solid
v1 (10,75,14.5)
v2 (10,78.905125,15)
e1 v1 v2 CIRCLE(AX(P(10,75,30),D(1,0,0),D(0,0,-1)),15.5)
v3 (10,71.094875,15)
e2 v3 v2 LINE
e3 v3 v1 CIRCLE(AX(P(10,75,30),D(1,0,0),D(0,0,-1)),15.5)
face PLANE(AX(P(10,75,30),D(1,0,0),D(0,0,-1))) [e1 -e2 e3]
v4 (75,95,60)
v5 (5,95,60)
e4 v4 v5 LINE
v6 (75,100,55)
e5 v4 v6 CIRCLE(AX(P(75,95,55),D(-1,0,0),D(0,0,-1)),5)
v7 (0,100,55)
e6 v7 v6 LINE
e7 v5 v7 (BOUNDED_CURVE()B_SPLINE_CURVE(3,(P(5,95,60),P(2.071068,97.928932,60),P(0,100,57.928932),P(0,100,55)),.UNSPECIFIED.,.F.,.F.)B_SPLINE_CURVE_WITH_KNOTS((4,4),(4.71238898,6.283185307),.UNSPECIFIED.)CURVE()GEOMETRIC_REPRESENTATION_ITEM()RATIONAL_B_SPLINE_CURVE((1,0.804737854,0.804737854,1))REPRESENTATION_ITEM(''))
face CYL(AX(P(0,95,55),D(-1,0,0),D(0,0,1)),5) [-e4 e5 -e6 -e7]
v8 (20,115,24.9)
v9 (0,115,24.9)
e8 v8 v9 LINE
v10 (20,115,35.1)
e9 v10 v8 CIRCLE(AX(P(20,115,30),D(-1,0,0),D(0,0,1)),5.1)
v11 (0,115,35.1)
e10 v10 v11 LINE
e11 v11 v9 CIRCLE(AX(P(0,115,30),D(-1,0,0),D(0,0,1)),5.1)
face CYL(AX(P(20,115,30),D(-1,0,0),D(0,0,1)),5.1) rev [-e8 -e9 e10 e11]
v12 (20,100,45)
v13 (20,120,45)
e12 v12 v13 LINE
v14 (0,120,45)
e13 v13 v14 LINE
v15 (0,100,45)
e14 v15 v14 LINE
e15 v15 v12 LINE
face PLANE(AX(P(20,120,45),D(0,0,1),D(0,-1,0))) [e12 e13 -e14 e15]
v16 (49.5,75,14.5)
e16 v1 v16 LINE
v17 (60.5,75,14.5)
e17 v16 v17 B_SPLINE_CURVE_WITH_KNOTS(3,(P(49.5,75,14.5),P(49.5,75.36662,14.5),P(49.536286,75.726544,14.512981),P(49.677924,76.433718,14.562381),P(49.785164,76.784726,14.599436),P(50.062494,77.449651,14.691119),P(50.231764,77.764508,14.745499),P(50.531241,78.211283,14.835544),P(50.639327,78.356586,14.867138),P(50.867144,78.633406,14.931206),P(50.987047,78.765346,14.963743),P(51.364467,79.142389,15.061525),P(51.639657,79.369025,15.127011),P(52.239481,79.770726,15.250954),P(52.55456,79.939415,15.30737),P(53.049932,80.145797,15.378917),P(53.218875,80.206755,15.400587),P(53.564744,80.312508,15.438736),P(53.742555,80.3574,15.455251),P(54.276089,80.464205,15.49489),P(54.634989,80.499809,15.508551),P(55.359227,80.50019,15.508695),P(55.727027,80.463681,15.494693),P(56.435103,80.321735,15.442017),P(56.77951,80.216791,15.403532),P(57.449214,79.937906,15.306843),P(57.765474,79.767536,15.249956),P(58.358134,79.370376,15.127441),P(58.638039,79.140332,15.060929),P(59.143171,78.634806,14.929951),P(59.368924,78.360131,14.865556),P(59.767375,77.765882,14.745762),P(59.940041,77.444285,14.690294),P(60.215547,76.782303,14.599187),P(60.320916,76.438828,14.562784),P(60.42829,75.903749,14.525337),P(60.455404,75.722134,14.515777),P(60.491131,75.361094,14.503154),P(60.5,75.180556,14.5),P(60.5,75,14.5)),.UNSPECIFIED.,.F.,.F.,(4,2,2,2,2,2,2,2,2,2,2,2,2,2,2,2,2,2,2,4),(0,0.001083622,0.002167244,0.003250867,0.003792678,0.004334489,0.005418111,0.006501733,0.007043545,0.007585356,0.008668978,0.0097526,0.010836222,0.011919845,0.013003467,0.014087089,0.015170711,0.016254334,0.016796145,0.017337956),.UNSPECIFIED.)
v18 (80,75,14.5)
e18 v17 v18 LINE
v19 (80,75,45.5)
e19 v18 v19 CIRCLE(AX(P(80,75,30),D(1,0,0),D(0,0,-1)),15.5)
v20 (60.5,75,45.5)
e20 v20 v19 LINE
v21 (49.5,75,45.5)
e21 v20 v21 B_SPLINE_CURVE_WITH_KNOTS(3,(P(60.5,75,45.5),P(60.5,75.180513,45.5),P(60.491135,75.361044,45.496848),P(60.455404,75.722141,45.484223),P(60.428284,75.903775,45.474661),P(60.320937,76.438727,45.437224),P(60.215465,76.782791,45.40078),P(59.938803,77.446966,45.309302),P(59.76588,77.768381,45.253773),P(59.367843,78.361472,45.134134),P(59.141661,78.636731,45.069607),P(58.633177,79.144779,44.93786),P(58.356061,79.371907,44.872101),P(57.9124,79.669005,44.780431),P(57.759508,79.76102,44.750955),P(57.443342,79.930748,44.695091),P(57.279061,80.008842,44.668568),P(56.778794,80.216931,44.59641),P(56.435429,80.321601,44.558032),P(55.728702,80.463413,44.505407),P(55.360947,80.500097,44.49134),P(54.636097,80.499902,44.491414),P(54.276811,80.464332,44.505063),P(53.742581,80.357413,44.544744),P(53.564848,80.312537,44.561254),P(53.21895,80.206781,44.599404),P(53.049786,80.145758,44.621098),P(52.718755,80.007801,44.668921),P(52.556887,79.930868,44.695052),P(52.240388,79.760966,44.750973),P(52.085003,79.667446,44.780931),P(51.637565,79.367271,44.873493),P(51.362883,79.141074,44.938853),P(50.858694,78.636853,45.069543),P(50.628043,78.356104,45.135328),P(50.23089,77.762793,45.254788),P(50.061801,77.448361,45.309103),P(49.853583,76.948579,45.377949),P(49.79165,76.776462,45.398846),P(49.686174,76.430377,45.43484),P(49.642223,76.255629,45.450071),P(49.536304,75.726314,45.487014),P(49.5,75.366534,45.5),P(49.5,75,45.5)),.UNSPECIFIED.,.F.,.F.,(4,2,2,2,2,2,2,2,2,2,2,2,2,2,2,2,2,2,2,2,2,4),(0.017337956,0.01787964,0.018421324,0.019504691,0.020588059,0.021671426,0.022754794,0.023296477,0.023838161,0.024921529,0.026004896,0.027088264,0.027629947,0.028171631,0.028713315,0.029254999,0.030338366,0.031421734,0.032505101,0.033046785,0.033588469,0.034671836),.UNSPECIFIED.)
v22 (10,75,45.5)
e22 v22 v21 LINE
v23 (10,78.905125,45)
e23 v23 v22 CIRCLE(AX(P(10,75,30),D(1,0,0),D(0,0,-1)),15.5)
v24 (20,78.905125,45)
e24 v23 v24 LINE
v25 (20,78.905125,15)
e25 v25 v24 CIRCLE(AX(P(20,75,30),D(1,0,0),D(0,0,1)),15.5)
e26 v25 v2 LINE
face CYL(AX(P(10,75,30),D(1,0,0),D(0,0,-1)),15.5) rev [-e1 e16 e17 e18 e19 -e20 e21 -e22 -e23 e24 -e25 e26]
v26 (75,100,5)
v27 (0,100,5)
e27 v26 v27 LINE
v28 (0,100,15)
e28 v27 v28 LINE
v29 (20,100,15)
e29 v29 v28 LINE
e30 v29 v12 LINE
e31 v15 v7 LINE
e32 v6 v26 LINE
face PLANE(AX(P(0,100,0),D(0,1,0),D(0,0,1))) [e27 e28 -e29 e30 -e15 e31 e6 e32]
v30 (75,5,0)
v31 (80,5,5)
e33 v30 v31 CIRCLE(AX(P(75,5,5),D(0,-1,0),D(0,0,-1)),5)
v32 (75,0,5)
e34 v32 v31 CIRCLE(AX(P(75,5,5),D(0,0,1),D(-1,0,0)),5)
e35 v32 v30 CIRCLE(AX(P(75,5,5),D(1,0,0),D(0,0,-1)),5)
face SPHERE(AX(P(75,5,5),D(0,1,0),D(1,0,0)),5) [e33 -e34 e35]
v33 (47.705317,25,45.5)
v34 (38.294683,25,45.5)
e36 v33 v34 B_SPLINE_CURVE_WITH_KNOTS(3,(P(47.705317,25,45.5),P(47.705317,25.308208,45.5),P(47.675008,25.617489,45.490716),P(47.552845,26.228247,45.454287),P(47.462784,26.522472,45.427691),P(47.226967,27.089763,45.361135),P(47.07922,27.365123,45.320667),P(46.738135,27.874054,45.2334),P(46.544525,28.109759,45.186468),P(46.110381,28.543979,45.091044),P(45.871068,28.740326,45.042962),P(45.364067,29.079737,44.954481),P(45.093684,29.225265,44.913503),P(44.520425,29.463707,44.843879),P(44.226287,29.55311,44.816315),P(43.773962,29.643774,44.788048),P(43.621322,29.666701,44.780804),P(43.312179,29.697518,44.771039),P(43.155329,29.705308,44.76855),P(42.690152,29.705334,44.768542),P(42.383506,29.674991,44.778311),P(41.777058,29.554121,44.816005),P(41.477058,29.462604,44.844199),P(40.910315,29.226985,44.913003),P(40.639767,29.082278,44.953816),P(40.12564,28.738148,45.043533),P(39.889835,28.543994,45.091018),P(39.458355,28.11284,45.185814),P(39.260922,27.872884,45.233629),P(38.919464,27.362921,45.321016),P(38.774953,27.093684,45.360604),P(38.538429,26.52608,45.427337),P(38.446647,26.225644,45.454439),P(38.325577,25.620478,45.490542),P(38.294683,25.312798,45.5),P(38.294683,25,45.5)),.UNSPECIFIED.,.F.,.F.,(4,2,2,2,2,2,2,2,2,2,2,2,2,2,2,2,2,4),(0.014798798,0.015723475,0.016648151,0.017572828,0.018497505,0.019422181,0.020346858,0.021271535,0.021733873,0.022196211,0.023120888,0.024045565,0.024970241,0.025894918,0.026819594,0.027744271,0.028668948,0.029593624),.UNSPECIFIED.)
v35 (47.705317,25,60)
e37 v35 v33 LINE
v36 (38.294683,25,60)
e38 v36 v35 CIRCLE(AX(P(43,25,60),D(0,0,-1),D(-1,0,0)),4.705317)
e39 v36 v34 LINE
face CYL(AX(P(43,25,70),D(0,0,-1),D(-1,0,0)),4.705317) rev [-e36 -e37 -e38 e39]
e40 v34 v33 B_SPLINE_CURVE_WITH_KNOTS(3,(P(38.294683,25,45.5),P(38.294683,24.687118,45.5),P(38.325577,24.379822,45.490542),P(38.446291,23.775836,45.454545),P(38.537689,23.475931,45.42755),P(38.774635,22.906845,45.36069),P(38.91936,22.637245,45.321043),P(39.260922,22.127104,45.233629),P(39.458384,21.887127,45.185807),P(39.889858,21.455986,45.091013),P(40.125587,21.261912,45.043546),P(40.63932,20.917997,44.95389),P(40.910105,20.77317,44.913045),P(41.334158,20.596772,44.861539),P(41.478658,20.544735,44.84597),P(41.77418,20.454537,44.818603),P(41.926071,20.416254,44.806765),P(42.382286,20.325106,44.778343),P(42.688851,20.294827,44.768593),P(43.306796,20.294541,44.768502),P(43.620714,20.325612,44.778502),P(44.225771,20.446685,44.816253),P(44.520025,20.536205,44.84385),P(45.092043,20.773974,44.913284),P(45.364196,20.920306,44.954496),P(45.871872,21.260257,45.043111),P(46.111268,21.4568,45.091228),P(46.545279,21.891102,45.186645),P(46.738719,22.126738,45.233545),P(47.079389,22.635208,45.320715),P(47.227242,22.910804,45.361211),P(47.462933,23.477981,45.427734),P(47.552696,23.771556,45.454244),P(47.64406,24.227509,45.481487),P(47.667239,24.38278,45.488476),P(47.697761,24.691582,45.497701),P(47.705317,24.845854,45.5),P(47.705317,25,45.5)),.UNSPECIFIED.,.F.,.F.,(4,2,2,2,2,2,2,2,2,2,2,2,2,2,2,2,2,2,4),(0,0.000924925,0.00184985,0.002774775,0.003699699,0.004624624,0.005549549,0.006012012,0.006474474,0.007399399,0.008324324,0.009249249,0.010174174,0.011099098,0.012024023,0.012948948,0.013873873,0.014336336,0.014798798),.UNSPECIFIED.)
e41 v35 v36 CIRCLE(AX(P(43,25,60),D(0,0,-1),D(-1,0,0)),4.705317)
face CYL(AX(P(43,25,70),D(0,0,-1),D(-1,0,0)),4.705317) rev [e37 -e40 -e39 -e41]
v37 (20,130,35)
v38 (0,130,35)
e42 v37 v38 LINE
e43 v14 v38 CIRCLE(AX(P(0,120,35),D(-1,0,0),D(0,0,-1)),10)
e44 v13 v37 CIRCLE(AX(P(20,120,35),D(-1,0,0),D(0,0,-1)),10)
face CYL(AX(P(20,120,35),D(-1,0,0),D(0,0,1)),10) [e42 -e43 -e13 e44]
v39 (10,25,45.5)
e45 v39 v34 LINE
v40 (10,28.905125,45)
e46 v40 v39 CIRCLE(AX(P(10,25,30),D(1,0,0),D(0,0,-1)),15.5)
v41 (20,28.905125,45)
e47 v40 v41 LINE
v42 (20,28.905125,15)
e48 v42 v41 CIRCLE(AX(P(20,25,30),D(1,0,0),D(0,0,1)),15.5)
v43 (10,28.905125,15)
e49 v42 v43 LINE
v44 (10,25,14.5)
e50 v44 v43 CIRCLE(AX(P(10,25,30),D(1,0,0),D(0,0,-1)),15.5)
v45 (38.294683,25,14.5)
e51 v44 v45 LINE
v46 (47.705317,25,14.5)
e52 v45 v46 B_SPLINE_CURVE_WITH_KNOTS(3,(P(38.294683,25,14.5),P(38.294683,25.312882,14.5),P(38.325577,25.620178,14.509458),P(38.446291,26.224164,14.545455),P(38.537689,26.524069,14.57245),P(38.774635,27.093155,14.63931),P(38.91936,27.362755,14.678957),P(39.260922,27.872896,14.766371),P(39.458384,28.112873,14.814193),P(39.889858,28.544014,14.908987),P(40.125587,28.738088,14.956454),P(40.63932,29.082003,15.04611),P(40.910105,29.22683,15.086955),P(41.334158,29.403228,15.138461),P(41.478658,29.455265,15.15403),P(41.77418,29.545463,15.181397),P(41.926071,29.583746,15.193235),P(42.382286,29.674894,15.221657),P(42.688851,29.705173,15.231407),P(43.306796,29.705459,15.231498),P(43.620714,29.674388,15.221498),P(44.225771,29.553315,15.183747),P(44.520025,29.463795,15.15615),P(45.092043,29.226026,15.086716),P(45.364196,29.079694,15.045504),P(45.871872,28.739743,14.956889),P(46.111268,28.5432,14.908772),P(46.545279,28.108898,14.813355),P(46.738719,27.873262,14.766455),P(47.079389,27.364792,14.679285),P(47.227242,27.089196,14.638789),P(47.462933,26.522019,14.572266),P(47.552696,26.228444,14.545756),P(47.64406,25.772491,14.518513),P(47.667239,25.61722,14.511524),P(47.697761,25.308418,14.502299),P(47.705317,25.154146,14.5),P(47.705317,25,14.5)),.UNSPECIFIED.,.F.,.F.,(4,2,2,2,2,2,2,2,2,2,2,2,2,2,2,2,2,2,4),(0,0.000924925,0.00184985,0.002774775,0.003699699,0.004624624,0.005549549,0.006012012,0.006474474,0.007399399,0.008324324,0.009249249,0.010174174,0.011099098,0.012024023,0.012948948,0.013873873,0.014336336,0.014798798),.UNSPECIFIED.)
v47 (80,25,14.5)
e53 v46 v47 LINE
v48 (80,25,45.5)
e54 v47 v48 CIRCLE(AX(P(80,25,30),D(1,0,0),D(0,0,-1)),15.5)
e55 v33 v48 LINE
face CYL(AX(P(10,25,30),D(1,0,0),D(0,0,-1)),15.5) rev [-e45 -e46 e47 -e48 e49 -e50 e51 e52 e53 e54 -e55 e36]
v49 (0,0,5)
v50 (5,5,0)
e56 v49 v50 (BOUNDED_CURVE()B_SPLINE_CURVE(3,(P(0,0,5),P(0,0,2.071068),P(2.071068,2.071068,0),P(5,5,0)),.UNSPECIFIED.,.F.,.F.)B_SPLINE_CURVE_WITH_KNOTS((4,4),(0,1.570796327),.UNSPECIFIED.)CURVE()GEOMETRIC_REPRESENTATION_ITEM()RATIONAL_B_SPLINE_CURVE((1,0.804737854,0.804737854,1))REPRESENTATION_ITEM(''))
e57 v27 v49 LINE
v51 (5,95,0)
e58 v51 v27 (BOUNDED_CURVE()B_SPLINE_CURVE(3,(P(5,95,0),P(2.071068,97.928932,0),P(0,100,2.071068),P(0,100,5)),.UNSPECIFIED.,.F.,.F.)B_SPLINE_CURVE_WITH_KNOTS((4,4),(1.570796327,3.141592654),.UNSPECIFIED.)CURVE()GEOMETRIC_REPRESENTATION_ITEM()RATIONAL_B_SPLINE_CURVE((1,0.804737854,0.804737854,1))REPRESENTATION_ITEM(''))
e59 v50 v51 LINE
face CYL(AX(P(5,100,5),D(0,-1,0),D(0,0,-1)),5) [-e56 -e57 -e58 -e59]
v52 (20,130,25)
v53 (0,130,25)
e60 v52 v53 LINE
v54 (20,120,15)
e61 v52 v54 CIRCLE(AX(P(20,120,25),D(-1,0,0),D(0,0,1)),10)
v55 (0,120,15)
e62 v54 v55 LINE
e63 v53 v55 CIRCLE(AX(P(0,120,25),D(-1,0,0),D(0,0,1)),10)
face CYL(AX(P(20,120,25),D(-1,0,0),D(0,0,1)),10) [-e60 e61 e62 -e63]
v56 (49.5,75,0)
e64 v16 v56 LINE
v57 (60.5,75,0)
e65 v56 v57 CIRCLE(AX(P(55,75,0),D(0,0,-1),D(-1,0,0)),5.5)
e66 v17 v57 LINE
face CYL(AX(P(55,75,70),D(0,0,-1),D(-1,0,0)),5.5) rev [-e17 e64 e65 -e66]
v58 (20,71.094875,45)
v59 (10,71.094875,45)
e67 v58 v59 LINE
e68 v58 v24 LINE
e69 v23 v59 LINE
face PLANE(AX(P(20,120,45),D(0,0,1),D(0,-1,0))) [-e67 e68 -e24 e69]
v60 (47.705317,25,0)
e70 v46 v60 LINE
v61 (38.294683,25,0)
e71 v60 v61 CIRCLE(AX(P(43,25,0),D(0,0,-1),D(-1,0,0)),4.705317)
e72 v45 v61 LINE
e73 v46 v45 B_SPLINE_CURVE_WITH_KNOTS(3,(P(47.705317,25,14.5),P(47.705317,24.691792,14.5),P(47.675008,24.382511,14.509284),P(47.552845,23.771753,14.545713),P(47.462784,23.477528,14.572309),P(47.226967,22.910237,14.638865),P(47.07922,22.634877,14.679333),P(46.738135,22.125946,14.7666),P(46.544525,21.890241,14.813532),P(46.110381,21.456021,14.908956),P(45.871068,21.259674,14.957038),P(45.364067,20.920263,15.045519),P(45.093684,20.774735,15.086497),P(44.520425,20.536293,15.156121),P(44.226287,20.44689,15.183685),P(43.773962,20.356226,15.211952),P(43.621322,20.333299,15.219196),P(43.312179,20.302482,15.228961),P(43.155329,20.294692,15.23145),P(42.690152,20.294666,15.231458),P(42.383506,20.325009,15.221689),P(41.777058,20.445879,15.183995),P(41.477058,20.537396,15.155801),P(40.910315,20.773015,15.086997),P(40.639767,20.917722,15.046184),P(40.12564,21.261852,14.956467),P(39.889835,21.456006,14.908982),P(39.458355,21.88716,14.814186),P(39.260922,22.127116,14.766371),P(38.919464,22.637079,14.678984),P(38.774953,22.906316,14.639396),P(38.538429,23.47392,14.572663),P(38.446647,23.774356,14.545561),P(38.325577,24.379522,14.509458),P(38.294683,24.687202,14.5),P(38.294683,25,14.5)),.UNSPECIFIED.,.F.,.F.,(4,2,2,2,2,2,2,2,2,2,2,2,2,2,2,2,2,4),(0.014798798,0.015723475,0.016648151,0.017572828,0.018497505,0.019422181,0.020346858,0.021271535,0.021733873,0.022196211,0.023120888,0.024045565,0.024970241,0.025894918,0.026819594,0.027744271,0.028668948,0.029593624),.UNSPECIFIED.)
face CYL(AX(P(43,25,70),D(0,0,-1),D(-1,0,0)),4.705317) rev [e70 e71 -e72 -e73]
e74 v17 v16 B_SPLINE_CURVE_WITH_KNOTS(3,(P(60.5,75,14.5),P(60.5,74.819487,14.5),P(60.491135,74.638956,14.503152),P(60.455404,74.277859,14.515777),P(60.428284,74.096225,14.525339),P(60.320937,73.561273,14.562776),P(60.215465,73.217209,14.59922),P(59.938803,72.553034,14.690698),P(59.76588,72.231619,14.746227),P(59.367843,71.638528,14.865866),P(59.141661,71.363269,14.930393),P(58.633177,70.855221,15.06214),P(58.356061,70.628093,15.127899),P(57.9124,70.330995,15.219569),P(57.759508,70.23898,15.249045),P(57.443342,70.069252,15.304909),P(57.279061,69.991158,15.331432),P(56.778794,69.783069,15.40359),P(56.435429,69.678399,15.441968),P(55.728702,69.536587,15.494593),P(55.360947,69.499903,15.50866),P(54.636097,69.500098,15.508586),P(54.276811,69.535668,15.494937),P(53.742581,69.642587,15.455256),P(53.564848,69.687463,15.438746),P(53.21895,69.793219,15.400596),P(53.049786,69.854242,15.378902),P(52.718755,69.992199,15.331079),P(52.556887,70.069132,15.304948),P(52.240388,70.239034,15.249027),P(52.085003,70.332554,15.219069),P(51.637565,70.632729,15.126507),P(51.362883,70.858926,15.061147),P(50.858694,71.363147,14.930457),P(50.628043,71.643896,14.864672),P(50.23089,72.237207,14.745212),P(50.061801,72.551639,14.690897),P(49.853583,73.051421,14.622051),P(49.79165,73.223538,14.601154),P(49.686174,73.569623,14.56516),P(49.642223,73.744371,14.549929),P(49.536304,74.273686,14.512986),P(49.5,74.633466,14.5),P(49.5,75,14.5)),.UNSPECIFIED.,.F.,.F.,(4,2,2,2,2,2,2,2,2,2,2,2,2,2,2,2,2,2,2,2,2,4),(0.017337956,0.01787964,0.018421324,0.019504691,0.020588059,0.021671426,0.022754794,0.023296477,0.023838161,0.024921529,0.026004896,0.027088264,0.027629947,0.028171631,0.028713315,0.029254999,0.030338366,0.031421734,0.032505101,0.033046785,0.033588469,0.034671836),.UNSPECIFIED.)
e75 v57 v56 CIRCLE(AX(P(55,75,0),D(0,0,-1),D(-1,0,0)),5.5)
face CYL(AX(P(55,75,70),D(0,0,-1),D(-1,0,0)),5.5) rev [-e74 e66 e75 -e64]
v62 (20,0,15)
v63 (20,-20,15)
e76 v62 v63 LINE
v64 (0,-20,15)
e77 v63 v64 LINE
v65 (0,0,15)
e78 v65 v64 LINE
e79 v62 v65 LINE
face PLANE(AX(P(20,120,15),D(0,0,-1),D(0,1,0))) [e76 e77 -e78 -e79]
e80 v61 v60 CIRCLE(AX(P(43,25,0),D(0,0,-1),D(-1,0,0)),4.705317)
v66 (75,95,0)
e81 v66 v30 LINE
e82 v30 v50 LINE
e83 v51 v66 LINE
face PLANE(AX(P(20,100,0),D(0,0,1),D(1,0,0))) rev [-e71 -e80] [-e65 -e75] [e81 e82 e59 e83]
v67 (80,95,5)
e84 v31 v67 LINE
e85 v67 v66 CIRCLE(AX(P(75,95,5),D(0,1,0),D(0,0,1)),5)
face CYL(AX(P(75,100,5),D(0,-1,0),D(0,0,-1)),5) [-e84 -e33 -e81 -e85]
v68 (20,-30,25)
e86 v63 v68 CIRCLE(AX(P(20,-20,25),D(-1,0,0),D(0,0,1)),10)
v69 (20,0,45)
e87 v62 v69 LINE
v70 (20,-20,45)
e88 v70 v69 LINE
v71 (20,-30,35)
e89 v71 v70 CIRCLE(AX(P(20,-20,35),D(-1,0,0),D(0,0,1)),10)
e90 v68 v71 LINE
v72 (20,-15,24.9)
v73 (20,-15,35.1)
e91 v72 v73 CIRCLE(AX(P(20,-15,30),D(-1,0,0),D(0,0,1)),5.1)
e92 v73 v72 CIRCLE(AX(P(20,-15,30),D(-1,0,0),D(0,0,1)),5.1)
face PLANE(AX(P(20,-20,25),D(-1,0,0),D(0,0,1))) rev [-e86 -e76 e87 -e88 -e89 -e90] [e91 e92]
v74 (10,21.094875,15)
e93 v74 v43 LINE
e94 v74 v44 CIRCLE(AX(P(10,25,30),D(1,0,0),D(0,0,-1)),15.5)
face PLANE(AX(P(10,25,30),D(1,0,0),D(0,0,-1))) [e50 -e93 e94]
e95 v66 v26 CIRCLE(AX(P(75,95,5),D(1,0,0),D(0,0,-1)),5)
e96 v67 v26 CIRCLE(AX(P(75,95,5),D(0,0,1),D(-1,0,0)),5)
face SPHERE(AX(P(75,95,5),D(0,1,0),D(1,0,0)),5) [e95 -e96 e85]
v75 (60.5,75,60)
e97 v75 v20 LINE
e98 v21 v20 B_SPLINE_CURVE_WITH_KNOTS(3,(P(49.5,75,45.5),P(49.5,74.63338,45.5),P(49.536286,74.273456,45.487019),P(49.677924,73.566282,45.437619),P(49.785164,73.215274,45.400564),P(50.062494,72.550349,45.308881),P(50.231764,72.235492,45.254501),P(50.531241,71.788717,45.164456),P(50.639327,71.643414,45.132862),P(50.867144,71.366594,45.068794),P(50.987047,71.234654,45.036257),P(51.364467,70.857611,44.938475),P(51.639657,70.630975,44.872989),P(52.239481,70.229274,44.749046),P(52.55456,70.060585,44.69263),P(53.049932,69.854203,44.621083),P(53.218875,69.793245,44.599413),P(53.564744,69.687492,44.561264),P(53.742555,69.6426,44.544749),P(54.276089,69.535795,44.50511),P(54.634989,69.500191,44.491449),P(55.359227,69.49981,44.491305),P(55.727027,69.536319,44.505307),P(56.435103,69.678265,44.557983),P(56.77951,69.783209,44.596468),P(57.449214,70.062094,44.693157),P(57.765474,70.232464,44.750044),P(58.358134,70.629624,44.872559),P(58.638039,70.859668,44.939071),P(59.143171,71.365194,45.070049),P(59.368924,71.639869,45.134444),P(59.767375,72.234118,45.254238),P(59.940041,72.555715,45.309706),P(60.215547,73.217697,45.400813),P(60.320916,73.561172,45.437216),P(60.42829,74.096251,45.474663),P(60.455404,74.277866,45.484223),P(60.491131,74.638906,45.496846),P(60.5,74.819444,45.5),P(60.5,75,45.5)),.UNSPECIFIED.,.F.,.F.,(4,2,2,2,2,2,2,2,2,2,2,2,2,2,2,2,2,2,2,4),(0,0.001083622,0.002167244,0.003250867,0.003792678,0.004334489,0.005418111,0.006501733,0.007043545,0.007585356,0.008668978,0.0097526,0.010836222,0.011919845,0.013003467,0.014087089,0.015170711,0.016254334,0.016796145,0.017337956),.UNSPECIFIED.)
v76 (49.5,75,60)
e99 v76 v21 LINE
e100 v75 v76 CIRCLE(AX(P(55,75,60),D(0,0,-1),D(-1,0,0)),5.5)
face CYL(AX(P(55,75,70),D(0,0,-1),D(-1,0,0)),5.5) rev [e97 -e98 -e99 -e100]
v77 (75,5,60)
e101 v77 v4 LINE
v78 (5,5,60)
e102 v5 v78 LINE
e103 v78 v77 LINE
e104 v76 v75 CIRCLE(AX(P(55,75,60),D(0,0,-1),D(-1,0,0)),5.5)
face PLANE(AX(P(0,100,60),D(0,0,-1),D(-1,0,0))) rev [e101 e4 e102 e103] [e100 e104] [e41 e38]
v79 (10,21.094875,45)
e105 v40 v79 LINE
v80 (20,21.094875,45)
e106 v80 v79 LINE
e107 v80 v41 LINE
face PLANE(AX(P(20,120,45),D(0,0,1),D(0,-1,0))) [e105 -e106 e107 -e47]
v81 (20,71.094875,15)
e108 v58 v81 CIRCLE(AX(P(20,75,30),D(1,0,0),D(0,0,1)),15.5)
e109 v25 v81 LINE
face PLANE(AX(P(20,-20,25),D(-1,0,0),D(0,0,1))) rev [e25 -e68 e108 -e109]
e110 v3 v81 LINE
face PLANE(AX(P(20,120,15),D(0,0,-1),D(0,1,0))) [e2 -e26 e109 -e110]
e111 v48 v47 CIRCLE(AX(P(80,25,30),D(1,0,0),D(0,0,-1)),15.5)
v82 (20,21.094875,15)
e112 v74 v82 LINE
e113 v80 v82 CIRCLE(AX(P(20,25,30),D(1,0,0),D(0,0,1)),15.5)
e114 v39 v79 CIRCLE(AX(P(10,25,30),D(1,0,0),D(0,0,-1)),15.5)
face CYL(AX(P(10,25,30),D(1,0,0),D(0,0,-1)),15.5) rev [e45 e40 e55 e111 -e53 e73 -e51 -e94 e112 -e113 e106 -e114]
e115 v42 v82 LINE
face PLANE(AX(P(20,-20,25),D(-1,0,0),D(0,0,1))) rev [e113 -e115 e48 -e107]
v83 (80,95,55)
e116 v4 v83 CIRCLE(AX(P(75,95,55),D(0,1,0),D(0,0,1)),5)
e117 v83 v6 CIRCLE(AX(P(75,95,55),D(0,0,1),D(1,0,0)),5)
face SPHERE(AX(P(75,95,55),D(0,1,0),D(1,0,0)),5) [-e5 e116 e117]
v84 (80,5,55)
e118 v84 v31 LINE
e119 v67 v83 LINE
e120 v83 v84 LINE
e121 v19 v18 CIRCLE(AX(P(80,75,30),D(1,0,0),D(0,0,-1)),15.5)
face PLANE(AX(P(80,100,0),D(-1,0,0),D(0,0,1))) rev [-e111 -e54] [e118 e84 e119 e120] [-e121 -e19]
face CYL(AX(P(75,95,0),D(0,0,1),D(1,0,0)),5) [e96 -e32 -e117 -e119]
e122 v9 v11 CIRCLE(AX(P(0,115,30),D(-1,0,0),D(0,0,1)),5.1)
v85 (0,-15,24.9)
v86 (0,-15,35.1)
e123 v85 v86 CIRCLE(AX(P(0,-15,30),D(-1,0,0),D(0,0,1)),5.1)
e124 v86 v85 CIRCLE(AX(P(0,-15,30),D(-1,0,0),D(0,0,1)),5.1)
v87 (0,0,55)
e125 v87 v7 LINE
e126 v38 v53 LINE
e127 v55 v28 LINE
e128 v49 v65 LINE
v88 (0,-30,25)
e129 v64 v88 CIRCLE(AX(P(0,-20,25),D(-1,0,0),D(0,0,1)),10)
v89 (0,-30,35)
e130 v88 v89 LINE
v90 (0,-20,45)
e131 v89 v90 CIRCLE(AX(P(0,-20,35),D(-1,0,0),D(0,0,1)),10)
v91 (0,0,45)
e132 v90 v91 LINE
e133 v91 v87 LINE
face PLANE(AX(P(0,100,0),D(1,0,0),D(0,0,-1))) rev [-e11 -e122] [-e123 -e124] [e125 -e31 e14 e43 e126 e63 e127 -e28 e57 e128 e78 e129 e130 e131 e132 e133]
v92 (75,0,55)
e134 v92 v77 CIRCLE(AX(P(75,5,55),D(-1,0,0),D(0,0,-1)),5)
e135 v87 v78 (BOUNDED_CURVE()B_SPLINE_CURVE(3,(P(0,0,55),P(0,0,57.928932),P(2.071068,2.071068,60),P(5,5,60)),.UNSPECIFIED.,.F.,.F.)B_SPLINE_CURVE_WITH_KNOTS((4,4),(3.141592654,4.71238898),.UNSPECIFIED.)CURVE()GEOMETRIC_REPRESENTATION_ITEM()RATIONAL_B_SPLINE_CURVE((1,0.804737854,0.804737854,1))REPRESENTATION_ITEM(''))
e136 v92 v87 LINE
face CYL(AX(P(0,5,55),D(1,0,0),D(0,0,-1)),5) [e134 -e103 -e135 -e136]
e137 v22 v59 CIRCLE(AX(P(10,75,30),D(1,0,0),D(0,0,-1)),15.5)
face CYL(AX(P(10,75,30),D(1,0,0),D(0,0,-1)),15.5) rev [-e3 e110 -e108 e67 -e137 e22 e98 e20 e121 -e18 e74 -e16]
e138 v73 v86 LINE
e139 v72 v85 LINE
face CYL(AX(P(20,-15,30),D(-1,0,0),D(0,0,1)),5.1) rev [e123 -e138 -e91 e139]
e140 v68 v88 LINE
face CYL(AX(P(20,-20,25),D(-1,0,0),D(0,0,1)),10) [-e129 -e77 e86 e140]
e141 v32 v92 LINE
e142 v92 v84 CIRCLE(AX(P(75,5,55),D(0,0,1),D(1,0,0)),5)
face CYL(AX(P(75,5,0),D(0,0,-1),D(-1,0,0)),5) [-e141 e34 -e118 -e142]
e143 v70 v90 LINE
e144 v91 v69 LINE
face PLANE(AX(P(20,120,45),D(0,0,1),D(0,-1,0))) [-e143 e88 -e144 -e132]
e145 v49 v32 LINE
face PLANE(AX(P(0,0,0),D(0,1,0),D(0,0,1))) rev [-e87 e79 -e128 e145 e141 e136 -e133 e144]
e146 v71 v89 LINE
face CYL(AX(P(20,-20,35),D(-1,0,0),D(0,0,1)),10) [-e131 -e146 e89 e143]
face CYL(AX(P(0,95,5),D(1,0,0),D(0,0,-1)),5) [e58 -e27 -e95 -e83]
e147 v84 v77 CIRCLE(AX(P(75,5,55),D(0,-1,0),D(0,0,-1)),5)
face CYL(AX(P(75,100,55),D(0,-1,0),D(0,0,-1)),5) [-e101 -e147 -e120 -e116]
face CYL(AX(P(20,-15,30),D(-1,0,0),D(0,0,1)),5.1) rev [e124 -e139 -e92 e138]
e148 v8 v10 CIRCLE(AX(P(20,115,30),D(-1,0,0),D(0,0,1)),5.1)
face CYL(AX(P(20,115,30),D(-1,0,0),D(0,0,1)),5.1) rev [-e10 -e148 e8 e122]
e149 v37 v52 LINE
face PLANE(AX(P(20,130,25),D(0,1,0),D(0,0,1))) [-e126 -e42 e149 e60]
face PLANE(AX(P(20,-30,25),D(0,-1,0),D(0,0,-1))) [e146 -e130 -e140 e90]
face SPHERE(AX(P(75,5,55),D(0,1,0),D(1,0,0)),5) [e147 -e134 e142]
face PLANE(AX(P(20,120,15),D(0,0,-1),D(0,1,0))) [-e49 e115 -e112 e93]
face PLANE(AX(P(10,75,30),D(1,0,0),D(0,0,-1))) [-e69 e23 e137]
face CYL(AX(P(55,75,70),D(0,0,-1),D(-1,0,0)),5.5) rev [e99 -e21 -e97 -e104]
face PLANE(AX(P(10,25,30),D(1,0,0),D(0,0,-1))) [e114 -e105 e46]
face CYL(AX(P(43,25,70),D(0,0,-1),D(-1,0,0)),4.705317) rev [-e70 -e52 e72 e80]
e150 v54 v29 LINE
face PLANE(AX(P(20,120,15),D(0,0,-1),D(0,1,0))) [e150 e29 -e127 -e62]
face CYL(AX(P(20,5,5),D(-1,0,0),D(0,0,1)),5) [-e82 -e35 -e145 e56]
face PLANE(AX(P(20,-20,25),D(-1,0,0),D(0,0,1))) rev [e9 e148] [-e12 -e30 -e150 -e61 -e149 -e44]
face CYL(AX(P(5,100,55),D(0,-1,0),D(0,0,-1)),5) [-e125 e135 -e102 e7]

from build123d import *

# Parameters (mm, degrees)
BOSS_EXTRUDE1_DEPTH = 100
SKETCH2_R           = 15.5
CUT_EXTRUDE1_DEPTH  = 70
SKETCH3_R           = 5.1
CUT_EXTRUDE2_DEPTH  = 70
SKETCH4_R           = 5.5
SKETCH4_R_2         = 4.705316684
CUT_EXTRUDE3_DEPTH  = 70
SKETCH5_R           = 5.1
BOSS_EXTRUDE2_DEPTH = 20
SKETCH6_W           = 20
SKETCH6_H           = 100
CUT_EXTRUDE4_DEPTH  = 20
FILLET1_R           = 5


with BuildPart() as part:
    # Sketch1 → Boss-Extrude1 (new body)
    with BuildSketch(Plane(origin=(0, 0, 0), x_dir=(1, 0, 0), z_dir=(0, 1, 0))):
        Polygon((0, 20), (20, 20), (20, 0), (80, 0), (80, -60), (0, -60), (0, 0), align=None)
    extrude(amount=BOSS_EXTRUDE1_DEPTH)

    # Sketch2 → Cut-Extrude1 (cut)
    with BuildSketch(Plane(origin=(80, 0, 0), x_dir=(0, 0, -1), z_dir=(1, 0, 0))):
        with Locations((-30, 75)):
            Circle(SKETCH2_R)
        with Locations((-30, 25)):
            Circle(SKETCH2_R)
    extrude(amount=-CUT_EXTRUDE1_DEPTH, mode=Mode.SUBTRACT)

    # Sketch3 → Cut-Extrude2 (cut)
    with BuildSketch(Plane(origin=(20, 0, 0), x_dir=(0, 0, -1), z_dir=(1, 0, 0))):
        with Locations((10, 87.5)):
            Circle(SKETCH3_R)
        with Locations((10, 12.5)):
            Circle(SKETCH3_R)
        with Locations((10, 50)):
            Circle(SKETCH3_R)
    extrude(amount=-CUT_EXTRUDE2_DEPTH, mode=Mode.SUBTRACT)

    # Sketch4 → Cut-Extrude3 (cut)
    with BuildSketch(Plane(origin=(0, 0, 0), x_dir=(-1, 0, 0), z_dir=(0, 0, -1))):
        with Locations((-55, 75)):
            Circle(SKETCH4_R)
        with Locations((-43, 25)):
            Circle(SKETCH4_R_2)
    extrude(amount=-CUT_EXTRUDE3_DEPTH, mode=Mode.SUBTRACT)

    # Sketch5 → Boss-Extrude2 (add)
    with BuildSketch(Plane.ZY):
        with BuildLine():
            Line((25, 130), (35, 130))
            ThreePointArc((35, 130), (42.071067812, 127.071067812), (45, 120))
            Line((45, 120), (45, -20))
            ThreePointArc((45, -20), (42.071067812, -27.071067812), (35, -30))
            Line((35, -30), (25, -30))
            ThreePointArc((25, -30), (17.928932188, -27.071067812), (15, -20))
            Line((15, -20), (15, 120))
            ThreePointArc((15, 120), (17.928932188, 127.071067812), (25, 130))
        make_face()
        with Locations((30, 115)):
            Circle(SKETCH5_R, mode=Mode.SUBTRACT)
        with Locations((30, -15)):
            Circle(SKETCH5_R, mode=Mode.SUBTRACT)
    extrude(amount=-BOSS_EXTRUDE2_DEPTH)

    # Sketch6 → Cut-Extrude4 (cut)
    with BuildSketch(Plane(origin=(20, 0, 0), x_dir=(0, 0, -1), z_dir=(1, 0, 0))):
        with Locations((10, 50)):
            Rectangle(SKETCH6_W, SKETCH6_H)
    extrude(amount=-CUT_EXTRUDE4_DEPTH, mode=Mode.SUBTRACT)

    # Fillet1
    fillet1_edges = [part.edges().sort_by_distance(p)[0] for p in [
        (80, 100, 30),
        (80, 50, 0),
        (80, 50, 60),
        (0, 50, 60),
        (40, 100, 0),
        (0, 50, 0),
        (40, 100, 60),
        (40, 0, 0),
        (80, 0, 30),
        (40, 0, 60),
    ]]
    fillet(fillet1_edges, radius=FILLET1_R)


solid = part.part
